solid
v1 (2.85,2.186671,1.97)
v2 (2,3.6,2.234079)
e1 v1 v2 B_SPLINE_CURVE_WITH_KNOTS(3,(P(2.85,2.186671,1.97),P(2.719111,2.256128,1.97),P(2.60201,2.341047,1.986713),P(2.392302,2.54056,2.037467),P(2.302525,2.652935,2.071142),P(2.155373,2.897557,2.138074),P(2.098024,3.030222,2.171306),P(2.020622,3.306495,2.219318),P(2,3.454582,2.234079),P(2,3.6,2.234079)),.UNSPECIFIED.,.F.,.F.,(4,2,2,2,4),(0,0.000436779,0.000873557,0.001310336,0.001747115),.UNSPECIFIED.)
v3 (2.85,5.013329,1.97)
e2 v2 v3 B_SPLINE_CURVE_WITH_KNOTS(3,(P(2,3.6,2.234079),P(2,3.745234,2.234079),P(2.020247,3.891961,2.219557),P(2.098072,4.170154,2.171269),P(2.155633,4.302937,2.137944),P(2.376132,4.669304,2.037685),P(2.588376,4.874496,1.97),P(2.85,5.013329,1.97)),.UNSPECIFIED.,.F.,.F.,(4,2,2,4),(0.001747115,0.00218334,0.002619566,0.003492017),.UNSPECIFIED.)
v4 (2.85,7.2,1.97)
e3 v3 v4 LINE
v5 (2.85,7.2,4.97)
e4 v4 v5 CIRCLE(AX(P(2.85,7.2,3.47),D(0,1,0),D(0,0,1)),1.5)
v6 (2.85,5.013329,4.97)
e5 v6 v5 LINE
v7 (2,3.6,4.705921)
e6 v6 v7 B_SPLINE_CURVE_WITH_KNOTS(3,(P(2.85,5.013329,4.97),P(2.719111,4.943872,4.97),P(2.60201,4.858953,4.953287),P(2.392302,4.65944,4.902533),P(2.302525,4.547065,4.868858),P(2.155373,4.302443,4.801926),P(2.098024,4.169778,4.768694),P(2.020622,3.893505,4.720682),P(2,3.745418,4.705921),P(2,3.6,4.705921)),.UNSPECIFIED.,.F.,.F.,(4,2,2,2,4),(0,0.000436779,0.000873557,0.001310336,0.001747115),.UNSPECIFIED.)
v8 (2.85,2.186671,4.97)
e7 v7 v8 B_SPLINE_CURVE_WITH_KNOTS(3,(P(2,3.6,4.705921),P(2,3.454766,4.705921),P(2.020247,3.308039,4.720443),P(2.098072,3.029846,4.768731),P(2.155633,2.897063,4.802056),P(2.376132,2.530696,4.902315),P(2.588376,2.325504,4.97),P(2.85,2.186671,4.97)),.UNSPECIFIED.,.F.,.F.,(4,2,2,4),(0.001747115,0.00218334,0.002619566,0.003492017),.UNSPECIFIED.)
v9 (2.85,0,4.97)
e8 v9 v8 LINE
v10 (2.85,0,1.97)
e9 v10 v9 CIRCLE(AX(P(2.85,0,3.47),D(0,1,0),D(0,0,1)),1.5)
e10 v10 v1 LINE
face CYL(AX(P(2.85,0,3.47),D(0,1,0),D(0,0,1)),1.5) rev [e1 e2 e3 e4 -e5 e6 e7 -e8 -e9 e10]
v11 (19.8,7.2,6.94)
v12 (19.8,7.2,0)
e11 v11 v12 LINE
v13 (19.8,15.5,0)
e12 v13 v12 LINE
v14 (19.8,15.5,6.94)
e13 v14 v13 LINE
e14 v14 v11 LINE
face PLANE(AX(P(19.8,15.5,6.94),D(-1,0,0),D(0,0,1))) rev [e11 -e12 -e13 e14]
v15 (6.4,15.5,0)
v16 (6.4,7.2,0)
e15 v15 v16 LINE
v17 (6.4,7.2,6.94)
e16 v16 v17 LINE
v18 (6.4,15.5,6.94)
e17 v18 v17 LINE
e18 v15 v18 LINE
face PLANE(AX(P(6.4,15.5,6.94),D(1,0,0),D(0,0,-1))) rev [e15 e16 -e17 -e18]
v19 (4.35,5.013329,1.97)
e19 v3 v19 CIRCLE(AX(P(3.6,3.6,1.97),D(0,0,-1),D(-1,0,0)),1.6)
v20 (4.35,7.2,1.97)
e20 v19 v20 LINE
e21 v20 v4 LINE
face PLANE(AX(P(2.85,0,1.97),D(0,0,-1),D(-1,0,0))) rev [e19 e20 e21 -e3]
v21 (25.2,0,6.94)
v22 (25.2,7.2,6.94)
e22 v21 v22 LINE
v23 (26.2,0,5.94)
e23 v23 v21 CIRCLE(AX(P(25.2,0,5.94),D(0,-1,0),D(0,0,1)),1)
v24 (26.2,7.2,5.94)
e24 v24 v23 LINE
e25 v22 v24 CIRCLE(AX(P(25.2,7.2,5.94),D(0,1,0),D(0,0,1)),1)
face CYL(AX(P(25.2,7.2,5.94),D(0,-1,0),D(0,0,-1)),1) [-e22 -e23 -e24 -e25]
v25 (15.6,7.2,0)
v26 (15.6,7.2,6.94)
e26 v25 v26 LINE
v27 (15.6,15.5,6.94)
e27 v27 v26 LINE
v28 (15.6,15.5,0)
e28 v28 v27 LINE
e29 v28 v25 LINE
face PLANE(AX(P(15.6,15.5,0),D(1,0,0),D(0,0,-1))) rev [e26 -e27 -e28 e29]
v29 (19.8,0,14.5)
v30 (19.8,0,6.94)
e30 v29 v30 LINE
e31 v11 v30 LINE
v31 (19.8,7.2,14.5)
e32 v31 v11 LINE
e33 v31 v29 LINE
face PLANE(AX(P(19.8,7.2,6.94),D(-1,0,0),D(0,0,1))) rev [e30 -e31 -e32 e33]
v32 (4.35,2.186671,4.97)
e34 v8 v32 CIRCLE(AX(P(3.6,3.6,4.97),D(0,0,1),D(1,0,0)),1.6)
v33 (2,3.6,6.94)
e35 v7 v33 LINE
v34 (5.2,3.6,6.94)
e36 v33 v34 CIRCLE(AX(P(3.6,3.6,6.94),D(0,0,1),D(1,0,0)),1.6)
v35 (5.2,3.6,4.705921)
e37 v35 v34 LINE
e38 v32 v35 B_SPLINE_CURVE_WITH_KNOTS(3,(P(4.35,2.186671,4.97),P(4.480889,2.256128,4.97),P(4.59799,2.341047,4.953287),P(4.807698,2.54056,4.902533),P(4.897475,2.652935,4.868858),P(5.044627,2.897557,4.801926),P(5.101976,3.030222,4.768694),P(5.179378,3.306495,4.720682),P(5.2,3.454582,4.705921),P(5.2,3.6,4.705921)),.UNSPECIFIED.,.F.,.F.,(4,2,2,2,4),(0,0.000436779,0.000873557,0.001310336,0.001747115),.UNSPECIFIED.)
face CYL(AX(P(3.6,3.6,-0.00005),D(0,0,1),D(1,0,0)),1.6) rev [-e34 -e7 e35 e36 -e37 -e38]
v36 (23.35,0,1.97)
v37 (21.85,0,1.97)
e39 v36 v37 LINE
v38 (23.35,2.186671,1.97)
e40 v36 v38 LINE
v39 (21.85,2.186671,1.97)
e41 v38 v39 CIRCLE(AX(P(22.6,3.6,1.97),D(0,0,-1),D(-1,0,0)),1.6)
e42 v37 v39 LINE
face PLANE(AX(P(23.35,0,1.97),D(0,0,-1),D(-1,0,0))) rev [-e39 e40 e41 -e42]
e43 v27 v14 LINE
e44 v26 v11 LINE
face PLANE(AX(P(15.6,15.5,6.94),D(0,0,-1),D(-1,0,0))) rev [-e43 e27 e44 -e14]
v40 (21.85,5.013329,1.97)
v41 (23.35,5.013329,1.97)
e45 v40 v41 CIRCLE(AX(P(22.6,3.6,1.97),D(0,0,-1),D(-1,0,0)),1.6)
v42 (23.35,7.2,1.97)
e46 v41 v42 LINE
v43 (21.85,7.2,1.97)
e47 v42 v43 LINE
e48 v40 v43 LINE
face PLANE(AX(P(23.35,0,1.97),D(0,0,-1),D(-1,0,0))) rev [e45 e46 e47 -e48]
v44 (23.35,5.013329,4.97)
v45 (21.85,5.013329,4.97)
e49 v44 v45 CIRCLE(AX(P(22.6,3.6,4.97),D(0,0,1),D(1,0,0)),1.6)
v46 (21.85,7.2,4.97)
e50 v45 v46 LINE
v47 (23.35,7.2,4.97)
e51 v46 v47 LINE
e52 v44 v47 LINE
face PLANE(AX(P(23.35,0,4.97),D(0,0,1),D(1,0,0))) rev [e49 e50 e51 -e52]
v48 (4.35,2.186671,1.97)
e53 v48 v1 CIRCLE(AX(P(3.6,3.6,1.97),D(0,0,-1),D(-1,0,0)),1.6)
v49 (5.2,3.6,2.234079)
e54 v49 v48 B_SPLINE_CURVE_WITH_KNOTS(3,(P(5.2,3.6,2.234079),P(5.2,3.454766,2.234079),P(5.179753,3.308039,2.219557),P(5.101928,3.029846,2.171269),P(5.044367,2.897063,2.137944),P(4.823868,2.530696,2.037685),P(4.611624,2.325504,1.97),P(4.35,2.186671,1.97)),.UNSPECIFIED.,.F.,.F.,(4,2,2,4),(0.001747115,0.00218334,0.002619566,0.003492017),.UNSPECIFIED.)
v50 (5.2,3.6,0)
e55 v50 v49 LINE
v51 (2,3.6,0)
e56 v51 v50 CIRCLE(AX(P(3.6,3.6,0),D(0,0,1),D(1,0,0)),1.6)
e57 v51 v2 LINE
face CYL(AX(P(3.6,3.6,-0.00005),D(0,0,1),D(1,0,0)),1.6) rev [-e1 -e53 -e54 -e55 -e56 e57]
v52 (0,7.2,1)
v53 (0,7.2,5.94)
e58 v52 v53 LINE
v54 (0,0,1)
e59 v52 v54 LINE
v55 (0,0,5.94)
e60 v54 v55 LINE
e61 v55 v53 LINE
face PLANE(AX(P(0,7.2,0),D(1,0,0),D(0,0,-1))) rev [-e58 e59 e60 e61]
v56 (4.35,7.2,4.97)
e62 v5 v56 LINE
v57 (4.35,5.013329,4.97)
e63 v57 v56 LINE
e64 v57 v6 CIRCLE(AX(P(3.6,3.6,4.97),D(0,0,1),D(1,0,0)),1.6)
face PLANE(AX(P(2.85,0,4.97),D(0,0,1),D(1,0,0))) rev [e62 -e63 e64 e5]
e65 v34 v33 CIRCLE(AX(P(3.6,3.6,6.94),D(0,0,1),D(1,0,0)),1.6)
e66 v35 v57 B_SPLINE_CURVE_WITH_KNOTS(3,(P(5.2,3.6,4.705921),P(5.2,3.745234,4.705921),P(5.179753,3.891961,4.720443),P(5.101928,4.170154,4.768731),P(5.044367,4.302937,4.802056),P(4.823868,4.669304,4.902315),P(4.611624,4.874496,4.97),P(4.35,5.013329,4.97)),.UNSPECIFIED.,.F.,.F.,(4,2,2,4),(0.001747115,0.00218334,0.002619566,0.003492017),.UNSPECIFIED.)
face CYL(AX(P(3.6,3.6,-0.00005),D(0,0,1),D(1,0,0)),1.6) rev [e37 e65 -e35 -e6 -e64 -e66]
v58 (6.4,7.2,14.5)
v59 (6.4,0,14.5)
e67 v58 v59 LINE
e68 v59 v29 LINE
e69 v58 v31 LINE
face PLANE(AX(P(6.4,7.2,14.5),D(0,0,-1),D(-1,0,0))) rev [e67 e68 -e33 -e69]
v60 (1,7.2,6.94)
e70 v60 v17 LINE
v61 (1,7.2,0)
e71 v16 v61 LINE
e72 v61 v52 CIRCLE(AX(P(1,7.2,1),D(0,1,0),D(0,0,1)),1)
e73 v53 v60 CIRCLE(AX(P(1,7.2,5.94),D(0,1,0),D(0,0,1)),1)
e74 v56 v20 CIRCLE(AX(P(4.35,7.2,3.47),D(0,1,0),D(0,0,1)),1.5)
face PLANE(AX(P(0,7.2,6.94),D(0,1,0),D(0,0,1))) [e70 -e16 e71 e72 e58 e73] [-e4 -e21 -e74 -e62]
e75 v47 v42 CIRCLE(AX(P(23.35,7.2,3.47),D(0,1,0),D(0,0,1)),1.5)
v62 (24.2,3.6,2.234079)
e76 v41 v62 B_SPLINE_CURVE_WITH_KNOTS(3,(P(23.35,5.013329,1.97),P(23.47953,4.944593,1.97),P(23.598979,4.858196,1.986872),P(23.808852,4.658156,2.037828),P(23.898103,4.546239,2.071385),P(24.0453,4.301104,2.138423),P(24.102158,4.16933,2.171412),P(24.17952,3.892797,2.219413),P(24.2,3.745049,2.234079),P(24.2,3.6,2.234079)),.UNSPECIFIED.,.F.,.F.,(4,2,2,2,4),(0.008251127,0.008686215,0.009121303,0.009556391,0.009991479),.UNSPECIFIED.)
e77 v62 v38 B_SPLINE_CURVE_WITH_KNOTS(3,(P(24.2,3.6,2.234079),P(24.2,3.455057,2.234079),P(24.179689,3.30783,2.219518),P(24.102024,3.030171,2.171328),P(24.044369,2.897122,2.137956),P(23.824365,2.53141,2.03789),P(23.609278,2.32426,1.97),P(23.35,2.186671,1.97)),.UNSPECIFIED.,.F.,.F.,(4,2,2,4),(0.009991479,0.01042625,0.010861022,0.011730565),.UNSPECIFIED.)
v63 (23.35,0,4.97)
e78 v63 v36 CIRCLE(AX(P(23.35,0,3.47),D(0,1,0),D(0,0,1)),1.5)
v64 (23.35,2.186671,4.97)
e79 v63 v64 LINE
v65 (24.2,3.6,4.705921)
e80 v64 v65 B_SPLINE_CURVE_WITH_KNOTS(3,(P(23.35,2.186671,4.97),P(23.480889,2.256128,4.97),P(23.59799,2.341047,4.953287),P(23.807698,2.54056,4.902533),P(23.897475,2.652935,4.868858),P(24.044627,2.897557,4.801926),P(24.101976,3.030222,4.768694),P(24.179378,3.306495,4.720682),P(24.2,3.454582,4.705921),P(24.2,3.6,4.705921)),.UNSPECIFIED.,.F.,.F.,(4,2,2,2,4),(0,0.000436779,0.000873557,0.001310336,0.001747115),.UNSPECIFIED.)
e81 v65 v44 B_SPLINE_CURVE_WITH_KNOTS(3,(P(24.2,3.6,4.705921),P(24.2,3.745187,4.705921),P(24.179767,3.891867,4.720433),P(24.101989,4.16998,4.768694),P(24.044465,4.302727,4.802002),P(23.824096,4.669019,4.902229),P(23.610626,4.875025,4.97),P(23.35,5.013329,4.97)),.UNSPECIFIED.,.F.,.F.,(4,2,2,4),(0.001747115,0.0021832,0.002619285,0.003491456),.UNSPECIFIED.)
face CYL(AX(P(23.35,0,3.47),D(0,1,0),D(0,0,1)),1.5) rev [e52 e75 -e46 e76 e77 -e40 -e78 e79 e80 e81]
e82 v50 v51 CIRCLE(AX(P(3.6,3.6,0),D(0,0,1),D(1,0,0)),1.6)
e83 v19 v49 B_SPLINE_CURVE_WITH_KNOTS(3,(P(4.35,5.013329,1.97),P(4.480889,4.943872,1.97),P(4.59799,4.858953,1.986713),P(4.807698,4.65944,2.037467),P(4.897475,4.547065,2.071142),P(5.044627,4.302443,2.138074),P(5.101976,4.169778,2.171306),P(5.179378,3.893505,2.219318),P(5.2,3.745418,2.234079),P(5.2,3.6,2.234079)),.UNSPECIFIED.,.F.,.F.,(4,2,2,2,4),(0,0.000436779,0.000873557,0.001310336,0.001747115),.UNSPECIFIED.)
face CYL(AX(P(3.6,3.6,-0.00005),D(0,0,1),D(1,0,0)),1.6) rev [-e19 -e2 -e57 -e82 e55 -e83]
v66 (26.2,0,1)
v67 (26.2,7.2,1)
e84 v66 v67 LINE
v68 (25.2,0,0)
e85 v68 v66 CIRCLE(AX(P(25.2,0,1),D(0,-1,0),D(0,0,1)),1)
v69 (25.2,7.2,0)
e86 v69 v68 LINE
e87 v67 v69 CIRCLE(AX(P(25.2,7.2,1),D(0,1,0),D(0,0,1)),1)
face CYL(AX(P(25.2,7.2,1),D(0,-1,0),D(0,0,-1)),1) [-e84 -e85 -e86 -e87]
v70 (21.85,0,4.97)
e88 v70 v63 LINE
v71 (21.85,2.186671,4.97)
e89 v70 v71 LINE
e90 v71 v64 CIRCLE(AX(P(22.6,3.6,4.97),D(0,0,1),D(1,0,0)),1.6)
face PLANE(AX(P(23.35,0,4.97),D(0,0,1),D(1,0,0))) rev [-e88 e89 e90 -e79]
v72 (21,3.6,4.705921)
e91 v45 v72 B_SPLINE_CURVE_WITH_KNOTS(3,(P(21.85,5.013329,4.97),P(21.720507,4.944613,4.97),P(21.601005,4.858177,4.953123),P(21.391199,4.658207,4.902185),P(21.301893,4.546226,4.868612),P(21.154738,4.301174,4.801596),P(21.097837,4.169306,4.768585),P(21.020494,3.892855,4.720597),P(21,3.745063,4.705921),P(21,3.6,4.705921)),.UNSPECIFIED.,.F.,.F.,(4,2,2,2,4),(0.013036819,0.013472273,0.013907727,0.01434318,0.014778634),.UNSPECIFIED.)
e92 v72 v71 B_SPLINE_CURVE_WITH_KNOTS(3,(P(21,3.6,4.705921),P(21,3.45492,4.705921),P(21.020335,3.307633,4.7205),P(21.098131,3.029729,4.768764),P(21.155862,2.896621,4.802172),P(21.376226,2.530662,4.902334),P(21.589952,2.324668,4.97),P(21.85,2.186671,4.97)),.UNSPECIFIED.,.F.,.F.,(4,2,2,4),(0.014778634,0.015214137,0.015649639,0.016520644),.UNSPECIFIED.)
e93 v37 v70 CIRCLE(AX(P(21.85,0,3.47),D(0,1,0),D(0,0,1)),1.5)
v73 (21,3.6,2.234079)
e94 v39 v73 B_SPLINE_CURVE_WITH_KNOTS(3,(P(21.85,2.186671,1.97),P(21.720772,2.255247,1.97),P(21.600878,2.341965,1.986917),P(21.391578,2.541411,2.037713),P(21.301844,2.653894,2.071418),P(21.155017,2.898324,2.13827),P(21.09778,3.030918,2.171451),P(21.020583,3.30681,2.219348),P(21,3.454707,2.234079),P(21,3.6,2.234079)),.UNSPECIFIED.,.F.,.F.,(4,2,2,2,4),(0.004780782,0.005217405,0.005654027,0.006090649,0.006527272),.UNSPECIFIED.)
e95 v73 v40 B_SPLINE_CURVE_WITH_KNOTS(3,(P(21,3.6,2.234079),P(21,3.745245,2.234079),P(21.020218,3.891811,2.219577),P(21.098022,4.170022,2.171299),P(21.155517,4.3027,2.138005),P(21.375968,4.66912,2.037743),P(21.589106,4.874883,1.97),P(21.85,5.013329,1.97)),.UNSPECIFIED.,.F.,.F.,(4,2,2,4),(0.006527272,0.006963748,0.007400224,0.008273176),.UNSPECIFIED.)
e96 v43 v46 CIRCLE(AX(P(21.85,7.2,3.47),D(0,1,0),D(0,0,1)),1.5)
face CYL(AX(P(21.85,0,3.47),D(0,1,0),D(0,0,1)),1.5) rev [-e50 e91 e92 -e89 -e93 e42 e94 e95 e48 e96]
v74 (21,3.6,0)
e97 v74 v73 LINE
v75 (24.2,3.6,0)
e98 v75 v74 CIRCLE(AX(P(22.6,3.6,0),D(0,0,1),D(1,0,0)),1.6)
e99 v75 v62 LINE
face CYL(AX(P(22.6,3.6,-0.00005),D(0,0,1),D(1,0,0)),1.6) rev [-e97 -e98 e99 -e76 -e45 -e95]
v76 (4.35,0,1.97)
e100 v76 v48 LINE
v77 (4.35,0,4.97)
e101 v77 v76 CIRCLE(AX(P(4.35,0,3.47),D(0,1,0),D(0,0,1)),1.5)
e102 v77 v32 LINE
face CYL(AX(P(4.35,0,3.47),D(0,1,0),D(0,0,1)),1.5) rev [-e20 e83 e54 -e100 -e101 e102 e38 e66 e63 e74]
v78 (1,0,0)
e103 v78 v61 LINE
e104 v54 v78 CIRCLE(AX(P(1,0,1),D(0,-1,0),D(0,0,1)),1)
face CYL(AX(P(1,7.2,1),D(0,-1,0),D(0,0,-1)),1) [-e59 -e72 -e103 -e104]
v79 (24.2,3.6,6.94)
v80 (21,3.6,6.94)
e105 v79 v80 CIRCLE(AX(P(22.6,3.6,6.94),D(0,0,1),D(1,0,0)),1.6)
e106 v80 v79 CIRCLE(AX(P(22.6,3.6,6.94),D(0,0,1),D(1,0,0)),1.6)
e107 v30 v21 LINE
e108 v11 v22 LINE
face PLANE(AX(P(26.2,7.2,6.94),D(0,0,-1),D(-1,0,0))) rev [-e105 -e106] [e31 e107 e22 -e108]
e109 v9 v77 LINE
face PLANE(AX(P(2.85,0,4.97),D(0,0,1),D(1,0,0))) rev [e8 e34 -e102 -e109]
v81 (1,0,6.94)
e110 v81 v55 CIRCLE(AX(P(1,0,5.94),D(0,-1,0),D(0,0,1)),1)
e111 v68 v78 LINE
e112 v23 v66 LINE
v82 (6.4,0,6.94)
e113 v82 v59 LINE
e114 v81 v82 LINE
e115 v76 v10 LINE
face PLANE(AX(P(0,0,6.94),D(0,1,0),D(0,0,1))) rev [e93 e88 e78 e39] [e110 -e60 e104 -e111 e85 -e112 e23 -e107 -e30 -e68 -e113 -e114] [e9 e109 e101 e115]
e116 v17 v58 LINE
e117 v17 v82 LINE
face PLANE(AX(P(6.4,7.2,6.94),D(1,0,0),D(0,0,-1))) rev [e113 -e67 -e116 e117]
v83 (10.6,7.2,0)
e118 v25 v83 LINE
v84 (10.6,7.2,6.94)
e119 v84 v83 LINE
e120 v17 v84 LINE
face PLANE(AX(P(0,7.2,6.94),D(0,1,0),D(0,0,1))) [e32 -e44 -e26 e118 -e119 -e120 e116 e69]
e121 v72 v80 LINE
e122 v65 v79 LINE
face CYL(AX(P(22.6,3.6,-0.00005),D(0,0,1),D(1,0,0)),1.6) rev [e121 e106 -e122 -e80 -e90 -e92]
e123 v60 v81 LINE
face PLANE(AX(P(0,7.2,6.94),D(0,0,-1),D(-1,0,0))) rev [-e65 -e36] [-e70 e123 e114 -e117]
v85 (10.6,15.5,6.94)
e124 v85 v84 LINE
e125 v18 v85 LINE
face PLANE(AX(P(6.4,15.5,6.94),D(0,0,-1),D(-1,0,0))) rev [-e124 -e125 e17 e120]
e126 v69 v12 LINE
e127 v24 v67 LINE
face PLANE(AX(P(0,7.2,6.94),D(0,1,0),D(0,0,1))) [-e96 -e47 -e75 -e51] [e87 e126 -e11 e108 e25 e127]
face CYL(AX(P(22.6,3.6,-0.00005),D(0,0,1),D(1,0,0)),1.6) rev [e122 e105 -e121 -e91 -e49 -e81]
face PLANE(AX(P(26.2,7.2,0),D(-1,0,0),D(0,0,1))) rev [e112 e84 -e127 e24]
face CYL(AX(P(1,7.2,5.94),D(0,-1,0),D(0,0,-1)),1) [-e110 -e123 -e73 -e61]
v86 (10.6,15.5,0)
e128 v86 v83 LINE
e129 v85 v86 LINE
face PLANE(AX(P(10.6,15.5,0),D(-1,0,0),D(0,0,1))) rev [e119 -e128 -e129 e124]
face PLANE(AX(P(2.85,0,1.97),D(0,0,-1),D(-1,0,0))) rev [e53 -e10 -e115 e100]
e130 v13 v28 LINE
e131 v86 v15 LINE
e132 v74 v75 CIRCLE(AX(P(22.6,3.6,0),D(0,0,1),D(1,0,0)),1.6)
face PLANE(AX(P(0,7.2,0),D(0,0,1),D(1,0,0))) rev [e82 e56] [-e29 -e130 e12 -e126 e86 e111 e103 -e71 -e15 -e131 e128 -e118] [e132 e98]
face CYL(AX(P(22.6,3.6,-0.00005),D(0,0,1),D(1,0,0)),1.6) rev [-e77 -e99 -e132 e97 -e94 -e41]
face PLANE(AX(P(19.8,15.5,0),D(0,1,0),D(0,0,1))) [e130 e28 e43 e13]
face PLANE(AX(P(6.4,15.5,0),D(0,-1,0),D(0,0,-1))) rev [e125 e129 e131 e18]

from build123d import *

# Parameters (mm, degrees)
EXTRUDE_1_DEPTH     = 7.2
SKETCH_2_W          = 4.2
SKETCH_2_H          = 6.94
EXTRUDE_2_DEPTH     = 8.3
CUT_EXTRUDE_1_DEPTH = 32.073783162
SKETCH_4_R          = 1.6
CUT_EXTRUDE_2_DEPTH = 32.366281259
FILLET_1_R          = 1


with BuildPart() as part:
    # 草图1 → 凸台-拉伸1 (new body)
    with BuildSketch(Plane(origin=(0, 0, 0), x_dir=(1, 0, 0), z_dir=(0, 1, 0))):
        Polygon((0, -6.94), (6.4, -6.94), (6.4, -14.5), (19.8, -14.5), (19.8, -6.94), (26.2, -6.94), (26.2, 0), (0, 0), align=None)
    extrude(amount=EXTRUDE_1_DEPTH)

    # 草图2 → 凸台-拉伸2 (add)
    with BuildSketch(Plane(origin=(0, 7.2, 0), x_dir=(1, 0, 0), z_dir=(0, 1, 0))):
        with Locations((8.5, -3.47)):
            Rectangle(SKETCH_2_W, SKETCH_2_H)
        with Locations((17.7, -3.47)):
            Rectangle(SKETCH_2_W, SKETCH_2_H)
    extrude(amount=EXTRUDE_2_DEPTH)

    # 草图3 → 切除-拉伸1 (cut, through all)
    with BuildSketch(Plane(origin=(0, 7.2, 0), x_dir=(1, 0, 0), z_dir=(0, 1, 0))):
        with BuildLine():
            Line((2.85, -1.97), (4.35, -1.97))
            ThreePointArc((4.35, -1.97), (5.85, -3.47), (4.35, -4.97))
            Line((4.35, -4.97), (2.85, -4.97))
            ThreePointArc((2.85, -4.97), (1.35, -3.47), (2.85, -1.97))
        make_face()
        with BuildLine():
            Line((23.35, -4.97), (21.85, -4.97))
            ThreePointArc((21.85, -4.97), (20.35, -3.47), (21.85, -1.97))
            Line((21.85, -1.97), (23.35, -1.97))
            ThreePointArc((23.35, -1.97), (24.85, -3.47), (23.35, -4.97))
        make_face()
    extrude(amount=-CUT_EXTRUDE_1_DEPTH, mode=Mode.SUBTRACT)

    # 草图4 → 切除-拉伸2 (cut, through all)
    with BuildSketch(Plane.XY.offset(6.94)):
        with Locations((22.6, 3.6)):
            Circle(SKETCH_4_R)
        with Locations((3.6, 3.6)):
            Circle(SKETCH_4_R)
    extrude(amount=-CUT_EXTRUDE_2_DEPTH, mode=Mode.SUBTRACT)

    # 圆角1
    fillet_1_edges = [part.edges().sort_by_distance(p)[0] for p in [
        (0, 3.6, 0),
        (0, 3.6, 6.94),
        (26.2, 3.6, 0),
        (26.2, 3.6, 6.94),
    ]]
    fillet(fillet_1_edges, radius=FILLET_1_R)


solid = part.part
